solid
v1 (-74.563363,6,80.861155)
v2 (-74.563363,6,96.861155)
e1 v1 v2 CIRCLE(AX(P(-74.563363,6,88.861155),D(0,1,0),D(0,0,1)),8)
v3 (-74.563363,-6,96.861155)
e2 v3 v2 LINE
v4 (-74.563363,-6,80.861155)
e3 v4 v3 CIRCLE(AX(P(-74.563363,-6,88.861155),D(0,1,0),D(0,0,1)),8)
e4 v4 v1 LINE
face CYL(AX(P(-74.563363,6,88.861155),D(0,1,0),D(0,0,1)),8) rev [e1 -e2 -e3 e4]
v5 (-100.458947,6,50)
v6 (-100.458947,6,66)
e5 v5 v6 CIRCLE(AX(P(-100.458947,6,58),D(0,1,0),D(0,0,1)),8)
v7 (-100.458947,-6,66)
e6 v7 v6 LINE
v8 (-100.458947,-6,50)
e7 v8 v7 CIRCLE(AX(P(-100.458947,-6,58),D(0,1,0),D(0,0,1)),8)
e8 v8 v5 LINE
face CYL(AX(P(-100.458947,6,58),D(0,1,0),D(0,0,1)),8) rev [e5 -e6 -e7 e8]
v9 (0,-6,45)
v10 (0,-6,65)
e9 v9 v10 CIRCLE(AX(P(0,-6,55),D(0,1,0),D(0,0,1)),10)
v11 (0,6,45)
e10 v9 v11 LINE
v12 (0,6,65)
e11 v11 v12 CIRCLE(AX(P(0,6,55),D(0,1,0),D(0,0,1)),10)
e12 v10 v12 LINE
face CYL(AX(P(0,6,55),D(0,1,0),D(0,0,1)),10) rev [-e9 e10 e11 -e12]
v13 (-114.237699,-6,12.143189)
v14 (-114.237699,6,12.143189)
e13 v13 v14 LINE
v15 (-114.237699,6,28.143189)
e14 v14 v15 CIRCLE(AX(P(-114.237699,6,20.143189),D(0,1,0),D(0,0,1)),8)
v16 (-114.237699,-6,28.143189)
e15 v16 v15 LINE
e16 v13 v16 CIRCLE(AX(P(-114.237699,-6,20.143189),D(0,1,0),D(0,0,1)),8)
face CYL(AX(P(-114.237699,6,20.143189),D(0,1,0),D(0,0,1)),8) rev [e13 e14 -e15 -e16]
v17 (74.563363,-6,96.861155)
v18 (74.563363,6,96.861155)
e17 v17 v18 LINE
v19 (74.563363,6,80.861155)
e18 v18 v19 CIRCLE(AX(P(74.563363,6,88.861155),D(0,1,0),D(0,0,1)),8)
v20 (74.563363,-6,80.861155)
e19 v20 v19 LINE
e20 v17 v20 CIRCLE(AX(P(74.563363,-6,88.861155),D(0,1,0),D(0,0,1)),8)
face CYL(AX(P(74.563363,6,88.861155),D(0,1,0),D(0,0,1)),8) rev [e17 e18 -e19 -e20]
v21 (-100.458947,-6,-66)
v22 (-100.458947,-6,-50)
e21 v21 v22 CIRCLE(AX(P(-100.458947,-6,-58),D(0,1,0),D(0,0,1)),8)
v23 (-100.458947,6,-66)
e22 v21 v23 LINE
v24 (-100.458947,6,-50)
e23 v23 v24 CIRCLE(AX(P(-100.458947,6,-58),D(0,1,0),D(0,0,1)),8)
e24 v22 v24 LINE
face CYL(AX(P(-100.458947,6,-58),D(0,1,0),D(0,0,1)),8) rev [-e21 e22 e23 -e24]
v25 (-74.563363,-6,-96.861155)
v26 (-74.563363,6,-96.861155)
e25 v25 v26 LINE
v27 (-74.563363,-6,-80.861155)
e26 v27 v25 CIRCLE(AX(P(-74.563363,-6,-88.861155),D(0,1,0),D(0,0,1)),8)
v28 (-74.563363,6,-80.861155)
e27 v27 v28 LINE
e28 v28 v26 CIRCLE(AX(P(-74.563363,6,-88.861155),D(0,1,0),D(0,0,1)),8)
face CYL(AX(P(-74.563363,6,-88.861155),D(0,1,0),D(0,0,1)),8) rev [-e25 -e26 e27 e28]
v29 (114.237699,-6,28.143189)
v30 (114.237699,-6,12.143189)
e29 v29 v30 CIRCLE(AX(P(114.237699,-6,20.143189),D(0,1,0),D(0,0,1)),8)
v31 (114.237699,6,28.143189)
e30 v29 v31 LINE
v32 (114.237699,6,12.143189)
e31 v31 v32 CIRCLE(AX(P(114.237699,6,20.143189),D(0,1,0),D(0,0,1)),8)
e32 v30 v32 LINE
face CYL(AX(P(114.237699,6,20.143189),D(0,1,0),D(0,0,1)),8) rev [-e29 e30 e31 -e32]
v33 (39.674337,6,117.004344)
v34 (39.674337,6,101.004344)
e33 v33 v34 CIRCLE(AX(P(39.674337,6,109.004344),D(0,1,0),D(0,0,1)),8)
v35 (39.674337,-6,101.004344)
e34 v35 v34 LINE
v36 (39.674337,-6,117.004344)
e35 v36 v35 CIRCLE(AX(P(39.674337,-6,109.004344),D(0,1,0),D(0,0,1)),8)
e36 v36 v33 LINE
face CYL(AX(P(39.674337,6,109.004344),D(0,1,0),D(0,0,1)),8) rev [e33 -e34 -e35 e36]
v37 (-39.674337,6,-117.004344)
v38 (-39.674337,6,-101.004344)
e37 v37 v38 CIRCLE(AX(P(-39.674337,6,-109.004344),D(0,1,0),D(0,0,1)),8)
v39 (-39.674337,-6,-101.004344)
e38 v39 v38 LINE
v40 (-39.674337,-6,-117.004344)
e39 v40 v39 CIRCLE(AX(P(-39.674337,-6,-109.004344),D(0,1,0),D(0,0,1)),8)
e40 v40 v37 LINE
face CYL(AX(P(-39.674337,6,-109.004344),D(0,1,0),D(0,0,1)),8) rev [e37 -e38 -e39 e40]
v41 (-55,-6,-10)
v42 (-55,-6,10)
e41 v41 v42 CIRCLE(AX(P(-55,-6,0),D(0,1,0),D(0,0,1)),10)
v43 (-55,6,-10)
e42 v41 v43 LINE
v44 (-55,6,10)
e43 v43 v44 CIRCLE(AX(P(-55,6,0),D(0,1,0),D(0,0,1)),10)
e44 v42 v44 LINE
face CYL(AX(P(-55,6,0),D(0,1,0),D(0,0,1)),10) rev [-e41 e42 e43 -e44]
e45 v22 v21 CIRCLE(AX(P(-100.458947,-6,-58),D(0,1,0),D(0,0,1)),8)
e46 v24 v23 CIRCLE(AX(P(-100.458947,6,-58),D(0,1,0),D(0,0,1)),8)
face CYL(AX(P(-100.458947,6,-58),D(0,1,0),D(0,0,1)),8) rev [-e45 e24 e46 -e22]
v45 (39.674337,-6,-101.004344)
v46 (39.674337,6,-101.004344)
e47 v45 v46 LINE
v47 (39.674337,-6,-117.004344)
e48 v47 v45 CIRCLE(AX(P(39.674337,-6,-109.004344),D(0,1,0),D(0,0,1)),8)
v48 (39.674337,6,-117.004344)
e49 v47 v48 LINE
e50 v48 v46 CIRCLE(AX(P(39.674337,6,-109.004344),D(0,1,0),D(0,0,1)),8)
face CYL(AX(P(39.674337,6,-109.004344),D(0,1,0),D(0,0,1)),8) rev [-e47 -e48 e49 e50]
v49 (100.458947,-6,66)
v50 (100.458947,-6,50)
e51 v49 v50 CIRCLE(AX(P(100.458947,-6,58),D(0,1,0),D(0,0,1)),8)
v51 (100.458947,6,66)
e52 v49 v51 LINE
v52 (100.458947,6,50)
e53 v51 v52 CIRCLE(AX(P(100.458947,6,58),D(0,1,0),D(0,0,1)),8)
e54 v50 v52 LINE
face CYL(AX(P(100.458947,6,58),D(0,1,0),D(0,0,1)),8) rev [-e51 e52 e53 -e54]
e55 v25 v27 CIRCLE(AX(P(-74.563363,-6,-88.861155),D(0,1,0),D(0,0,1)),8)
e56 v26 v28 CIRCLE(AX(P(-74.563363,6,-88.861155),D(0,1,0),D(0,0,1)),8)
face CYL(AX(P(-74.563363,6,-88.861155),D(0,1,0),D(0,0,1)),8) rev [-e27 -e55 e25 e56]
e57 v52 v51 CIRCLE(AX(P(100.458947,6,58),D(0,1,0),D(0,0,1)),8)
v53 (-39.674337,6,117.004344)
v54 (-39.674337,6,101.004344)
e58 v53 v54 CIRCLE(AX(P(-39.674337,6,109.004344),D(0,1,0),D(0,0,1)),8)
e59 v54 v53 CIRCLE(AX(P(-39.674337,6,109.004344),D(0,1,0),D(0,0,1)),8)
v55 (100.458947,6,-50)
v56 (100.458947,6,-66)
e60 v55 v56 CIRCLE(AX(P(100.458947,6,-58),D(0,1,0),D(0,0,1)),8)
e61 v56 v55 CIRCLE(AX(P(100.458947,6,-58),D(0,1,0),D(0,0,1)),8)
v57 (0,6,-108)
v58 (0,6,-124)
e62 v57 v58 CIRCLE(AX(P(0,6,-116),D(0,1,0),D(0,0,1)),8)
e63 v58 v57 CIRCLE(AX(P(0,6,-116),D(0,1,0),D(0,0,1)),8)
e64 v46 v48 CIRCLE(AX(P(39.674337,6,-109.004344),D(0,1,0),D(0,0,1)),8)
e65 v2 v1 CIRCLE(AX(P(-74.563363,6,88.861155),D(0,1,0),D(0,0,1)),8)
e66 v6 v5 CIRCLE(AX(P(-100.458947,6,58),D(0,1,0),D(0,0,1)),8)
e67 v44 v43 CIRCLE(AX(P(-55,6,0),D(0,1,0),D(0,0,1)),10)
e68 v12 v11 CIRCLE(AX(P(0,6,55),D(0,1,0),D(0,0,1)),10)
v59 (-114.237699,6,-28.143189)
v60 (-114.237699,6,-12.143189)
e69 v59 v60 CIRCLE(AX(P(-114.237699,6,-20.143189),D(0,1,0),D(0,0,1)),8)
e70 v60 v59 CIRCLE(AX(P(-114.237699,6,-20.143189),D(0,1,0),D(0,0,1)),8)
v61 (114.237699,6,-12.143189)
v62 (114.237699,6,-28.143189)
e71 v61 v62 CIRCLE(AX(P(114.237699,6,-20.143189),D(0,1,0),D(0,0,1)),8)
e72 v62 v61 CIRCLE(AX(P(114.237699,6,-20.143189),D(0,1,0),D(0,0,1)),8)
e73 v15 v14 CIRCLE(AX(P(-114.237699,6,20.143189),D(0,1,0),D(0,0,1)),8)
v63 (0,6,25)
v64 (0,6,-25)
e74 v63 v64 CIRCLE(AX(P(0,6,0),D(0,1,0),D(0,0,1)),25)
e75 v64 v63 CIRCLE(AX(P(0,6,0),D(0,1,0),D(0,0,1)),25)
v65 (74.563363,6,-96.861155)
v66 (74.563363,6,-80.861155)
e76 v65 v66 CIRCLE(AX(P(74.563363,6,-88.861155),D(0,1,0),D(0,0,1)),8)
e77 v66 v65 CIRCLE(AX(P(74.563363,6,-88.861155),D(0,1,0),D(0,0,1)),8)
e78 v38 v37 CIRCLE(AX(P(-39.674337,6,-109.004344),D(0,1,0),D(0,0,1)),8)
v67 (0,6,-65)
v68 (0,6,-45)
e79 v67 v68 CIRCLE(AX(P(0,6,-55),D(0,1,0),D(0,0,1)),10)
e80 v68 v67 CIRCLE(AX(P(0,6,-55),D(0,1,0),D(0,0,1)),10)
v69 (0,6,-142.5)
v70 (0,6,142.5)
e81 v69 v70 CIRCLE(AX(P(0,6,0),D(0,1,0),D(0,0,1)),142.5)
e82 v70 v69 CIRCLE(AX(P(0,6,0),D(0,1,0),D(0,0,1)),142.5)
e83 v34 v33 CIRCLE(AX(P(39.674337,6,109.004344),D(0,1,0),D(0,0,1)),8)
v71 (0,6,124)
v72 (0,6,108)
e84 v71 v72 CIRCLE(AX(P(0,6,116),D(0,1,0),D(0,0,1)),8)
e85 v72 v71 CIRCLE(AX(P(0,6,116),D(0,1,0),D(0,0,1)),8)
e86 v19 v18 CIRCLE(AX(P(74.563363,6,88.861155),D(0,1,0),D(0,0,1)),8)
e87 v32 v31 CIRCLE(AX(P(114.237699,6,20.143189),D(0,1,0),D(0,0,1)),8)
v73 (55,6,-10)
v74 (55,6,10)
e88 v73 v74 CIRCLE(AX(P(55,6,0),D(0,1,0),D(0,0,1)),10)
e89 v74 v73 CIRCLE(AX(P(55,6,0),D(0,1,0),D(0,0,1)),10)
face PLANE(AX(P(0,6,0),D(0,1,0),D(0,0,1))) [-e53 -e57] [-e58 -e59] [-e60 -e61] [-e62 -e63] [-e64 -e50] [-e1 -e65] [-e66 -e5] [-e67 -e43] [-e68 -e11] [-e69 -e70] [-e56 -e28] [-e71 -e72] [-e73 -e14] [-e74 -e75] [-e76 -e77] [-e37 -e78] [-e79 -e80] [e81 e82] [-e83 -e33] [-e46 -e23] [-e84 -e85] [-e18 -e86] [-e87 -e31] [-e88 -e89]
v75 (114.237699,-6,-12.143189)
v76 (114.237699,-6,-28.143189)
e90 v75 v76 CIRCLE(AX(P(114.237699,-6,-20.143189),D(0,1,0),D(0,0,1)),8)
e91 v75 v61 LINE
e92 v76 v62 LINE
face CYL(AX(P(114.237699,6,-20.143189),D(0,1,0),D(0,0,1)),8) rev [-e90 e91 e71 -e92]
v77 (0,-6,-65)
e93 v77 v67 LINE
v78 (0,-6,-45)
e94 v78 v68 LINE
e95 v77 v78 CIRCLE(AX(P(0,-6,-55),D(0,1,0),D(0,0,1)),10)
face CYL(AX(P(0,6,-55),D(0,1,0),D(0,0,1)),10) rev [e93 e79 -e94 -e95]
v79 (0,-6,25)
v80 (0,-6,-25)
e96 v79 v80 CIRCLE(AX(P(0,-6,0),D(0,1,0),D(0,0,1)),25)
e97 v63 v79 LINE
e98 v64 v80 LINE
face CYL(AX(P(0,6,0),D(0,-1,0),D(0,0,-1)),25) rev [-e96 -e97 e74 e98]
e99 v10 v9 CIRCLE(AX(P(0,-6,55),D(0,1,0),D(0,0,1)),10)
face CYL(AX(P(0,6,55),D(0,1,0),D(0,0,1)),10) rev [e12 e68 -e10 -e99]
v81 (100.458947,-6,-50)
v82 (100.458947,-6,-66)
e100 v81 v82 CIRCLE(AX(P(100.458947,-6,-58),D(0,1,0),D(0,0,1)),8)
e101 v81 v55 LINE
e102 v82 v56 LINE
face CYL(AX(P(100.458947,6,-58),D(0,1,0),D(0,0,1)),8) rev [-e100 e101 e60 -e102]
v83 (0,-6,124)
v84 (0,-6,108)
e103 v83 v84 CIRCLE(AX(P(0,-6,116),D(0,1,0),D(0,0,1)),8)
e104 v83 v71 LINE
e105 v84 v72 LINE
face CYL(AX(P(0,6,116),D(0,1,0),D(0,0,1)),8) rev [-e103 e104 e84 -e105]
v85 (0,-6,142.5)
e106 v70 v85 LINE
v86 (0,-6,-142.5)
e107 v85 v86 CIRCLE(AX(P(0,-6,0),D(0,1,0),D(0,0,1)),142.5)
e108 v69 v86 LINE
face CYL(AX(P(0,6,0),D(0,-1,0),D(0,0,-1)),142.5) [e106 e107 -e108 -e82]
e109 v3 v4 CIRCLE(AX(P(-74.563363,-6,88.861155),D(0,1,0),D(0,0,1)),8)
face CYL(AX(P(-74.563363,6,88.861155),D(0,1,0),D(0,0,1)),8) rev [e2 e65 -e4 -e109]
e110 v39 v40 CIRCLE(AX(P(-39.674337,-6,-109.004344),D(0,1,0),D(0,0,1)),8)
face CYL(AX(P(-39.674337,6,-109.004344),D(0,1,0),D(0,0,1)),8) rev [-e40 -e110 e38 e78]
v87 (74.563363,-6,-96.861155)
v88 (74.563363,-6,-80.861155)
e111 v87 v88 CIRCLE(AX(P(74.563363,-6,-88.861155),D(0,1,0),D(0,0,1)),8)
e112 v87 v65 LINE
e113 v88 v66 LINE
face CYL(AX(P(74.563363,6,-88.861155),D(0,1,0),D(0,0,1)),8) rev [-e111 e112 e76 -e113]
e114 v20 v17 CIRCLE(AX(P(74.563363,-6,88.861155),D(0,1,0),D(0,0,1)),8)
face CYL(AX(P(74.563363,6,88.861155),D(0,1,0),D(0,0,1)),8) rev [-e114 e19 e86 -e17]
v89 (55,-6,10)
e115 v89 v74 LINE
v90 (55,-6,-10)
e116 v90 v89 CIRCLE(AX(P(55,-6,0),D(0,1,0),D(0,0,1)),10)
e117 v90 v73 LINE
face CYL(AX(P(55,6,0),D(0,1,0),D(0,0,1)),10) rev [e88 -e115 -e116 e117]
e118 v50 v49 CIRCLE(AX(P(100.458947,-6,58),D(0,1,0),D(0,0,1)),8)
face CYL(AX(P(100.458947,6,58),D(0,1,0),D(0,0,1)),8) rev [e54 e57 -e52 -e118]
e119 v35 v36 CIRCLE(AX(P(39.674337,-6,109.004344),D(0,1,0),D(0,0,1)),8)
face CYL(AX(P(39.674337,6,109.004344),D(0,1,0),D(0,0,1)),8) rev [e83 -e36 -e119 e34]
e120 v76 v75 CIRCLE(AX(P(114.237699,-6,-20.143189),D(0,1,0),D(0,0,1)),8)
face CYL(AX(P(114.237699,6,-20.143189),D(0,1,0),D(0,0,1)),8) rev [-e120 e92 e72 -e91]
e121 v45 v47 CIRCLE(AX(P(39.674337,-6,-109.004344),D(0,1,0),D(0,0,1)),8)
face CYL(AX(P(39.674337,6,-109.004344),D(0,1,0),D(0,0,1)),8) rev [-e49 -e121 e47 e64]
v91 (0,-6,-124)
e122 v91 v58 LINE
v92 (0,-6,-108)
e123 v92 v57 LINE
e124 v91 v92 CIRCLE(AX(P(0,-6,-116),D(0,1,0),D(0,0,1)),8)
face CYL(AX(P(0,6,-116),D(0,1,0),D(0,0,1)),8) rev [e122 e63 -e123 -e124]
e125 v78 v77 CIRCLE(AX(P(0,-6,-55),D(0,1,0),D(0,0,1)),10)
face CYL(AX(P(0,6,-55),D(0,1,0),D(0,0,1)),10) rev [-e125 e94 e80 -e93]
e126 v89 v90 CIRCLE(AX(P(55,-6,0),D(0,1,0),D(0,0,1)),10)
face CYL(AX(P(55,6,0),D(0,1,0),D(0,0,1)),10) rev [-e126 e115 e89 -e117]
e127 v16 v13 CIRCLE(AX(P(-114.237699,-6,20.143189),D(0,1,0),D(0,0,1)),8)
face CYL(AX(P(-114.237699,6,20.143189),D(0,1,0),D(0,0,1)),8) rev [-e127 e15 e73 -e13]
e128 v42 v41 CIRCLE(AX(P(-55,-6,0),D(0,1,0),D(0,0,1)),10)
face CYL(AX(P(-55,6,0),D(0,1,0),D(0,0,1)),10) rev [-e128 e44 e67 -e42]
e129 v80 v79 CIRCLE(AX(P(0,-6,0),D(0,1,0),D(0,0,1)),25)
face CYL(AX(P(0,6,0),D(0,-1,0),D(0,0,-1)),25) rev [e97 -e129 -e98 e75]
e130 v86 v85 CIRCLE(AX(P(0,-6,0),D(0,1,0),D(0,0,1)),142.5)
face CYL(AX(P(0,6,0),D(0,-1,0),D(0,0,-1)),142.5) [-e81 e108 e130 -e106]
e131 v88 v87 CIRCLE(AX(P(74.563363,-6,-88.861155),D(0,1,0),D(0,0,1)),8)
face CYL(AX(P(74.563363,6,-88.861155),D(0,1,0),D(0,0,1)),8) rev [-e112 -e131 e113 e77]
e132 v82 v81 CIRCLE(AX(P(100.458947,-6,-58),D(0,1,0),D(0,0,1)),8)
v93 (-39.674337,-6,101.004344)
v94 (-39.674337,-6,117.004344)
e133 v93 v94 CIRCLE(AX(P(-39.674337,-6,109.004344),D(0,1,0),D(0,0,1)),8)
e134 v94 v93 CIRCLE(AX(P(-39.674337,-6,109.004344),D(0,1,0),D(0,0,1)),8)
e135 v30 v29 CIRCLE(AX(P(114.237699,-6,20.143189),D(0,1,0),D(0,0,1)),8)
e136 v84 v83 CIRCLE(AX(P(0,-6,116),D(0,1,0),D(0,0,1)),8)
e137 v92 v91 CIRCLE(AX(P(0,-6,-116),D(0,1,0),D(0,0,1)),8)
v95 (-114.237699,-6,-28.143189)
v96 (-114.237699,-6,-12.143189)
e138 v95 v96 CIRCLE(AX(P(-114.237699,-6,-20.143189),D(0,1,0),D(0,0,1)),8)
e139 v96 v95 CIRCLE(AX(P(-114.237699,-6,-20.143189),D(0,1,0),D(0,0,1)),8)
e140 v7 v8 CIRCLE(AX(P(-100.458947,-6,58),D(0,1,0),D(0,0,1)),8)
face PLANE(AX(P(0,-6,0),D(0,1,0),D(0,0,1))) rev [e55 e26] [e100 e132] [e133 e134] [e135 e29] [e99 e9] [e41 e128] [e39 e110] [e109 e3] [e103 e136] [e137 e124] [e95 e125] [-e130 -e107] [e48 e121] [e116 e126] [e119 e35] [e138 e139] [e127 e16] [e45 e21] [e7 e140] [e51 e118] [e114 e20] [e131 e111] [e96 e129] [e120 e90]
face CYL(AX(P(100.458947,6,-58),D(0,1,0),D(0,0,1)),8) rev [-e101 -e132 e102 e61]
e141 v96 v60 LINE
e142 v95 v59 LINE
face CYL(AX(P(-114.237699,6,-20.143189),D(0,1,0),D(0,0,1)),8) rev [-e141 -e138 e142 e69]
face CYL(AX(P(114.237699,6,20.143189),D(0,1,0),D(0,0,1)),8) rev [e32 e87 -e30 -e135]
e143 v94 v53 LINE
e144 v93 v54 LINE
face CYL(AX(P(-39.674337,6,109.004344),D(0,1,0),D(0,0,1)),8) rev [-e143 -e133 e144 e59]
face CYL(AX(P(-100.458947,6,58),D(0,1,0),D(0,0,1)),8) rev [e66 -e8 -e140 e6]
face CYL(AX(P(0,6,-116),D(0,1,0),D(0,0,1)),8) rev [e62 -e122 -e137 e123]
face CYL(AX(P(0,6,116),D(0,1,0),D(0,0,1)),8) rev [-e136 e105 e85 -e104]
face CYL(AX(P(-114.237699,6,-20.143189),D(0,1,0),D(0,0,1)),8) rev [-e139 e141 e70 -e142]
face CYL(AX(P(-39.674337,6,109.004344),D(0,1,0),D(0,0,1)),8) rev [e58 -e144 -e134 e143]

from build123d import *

# Parameters (mm, degrees)
SKETCH1_R                  = 142.5
SKETCH1_R_2                = 25
BOSS_EXTRUDE1_DEPTH        = 6
F_20_0_20_DIAMETER_HOLE1_D = 20
F_16_0_16_DIAMETER_HOLE1_D = 16


with BuildPart() as part:
    # Sketch1 → Boss-Extrude1 (new, symmetric)
    with BuildSketch(Plane(origin=(0, 0, 0), x_dir=(1, 0, 0), z_dir=(0, 1, 0))):
        with Locations(Location((0, 0, 0), (0, 0, 270))):
            Circle(SKETCH1_R)
        with Locations(Location((0, 0, 0), (0, 0, 270))):
            Circle(SKETCH1_R_2, mode=Mode.SUBTRACT)
    extrude(amount=BOSS_EXTRUDE1_DEPTH, both=True)

    # Ø20.0 (20) Diameter Hole1 (through all)
    with Locations(Plane(origin=(0, 6, 0), x_dir=(1, 0, 0), z_dir=(0, 1, 0))):
        with Locations((0, 55), (55, 0), (0, -55), (-55, 0)):
            Hole(F_20_0_20_DIAMETER_HOLE1_D / 2)

    # Ø16.0 (16) Diameter Hole1 (through all)
    with Locations(Plane(origin=(0, 6, 0), x_dir=(1, 0, 0), z_dir=(0, 1, 0))):
        with Locations((0, 116), (39.674336626, 109.004344011), (74.563362724, 88.861155402), (100.458946839, 58), (114.237699349, 20.143188609), (114.237699349, -20.143188609), (100.458946839, -58), (74.563362724, -88.861155402), (39.674336626, -109.004344011), (0, -116), (-39.674336626, -109.004344011), (-74.563362724, -88.861155402), (-100.458946839, -58), (-114.237699349, -20.143188609), (-114.237699349, 20.143188609), (-100.458946839, 58), (-74.563362724, 88.861155402), (-39.674336626, 109.004344011)):
            Hole(F_16_0_16_DIAMETER_HOLE1_D / 2)


solid = part.part
